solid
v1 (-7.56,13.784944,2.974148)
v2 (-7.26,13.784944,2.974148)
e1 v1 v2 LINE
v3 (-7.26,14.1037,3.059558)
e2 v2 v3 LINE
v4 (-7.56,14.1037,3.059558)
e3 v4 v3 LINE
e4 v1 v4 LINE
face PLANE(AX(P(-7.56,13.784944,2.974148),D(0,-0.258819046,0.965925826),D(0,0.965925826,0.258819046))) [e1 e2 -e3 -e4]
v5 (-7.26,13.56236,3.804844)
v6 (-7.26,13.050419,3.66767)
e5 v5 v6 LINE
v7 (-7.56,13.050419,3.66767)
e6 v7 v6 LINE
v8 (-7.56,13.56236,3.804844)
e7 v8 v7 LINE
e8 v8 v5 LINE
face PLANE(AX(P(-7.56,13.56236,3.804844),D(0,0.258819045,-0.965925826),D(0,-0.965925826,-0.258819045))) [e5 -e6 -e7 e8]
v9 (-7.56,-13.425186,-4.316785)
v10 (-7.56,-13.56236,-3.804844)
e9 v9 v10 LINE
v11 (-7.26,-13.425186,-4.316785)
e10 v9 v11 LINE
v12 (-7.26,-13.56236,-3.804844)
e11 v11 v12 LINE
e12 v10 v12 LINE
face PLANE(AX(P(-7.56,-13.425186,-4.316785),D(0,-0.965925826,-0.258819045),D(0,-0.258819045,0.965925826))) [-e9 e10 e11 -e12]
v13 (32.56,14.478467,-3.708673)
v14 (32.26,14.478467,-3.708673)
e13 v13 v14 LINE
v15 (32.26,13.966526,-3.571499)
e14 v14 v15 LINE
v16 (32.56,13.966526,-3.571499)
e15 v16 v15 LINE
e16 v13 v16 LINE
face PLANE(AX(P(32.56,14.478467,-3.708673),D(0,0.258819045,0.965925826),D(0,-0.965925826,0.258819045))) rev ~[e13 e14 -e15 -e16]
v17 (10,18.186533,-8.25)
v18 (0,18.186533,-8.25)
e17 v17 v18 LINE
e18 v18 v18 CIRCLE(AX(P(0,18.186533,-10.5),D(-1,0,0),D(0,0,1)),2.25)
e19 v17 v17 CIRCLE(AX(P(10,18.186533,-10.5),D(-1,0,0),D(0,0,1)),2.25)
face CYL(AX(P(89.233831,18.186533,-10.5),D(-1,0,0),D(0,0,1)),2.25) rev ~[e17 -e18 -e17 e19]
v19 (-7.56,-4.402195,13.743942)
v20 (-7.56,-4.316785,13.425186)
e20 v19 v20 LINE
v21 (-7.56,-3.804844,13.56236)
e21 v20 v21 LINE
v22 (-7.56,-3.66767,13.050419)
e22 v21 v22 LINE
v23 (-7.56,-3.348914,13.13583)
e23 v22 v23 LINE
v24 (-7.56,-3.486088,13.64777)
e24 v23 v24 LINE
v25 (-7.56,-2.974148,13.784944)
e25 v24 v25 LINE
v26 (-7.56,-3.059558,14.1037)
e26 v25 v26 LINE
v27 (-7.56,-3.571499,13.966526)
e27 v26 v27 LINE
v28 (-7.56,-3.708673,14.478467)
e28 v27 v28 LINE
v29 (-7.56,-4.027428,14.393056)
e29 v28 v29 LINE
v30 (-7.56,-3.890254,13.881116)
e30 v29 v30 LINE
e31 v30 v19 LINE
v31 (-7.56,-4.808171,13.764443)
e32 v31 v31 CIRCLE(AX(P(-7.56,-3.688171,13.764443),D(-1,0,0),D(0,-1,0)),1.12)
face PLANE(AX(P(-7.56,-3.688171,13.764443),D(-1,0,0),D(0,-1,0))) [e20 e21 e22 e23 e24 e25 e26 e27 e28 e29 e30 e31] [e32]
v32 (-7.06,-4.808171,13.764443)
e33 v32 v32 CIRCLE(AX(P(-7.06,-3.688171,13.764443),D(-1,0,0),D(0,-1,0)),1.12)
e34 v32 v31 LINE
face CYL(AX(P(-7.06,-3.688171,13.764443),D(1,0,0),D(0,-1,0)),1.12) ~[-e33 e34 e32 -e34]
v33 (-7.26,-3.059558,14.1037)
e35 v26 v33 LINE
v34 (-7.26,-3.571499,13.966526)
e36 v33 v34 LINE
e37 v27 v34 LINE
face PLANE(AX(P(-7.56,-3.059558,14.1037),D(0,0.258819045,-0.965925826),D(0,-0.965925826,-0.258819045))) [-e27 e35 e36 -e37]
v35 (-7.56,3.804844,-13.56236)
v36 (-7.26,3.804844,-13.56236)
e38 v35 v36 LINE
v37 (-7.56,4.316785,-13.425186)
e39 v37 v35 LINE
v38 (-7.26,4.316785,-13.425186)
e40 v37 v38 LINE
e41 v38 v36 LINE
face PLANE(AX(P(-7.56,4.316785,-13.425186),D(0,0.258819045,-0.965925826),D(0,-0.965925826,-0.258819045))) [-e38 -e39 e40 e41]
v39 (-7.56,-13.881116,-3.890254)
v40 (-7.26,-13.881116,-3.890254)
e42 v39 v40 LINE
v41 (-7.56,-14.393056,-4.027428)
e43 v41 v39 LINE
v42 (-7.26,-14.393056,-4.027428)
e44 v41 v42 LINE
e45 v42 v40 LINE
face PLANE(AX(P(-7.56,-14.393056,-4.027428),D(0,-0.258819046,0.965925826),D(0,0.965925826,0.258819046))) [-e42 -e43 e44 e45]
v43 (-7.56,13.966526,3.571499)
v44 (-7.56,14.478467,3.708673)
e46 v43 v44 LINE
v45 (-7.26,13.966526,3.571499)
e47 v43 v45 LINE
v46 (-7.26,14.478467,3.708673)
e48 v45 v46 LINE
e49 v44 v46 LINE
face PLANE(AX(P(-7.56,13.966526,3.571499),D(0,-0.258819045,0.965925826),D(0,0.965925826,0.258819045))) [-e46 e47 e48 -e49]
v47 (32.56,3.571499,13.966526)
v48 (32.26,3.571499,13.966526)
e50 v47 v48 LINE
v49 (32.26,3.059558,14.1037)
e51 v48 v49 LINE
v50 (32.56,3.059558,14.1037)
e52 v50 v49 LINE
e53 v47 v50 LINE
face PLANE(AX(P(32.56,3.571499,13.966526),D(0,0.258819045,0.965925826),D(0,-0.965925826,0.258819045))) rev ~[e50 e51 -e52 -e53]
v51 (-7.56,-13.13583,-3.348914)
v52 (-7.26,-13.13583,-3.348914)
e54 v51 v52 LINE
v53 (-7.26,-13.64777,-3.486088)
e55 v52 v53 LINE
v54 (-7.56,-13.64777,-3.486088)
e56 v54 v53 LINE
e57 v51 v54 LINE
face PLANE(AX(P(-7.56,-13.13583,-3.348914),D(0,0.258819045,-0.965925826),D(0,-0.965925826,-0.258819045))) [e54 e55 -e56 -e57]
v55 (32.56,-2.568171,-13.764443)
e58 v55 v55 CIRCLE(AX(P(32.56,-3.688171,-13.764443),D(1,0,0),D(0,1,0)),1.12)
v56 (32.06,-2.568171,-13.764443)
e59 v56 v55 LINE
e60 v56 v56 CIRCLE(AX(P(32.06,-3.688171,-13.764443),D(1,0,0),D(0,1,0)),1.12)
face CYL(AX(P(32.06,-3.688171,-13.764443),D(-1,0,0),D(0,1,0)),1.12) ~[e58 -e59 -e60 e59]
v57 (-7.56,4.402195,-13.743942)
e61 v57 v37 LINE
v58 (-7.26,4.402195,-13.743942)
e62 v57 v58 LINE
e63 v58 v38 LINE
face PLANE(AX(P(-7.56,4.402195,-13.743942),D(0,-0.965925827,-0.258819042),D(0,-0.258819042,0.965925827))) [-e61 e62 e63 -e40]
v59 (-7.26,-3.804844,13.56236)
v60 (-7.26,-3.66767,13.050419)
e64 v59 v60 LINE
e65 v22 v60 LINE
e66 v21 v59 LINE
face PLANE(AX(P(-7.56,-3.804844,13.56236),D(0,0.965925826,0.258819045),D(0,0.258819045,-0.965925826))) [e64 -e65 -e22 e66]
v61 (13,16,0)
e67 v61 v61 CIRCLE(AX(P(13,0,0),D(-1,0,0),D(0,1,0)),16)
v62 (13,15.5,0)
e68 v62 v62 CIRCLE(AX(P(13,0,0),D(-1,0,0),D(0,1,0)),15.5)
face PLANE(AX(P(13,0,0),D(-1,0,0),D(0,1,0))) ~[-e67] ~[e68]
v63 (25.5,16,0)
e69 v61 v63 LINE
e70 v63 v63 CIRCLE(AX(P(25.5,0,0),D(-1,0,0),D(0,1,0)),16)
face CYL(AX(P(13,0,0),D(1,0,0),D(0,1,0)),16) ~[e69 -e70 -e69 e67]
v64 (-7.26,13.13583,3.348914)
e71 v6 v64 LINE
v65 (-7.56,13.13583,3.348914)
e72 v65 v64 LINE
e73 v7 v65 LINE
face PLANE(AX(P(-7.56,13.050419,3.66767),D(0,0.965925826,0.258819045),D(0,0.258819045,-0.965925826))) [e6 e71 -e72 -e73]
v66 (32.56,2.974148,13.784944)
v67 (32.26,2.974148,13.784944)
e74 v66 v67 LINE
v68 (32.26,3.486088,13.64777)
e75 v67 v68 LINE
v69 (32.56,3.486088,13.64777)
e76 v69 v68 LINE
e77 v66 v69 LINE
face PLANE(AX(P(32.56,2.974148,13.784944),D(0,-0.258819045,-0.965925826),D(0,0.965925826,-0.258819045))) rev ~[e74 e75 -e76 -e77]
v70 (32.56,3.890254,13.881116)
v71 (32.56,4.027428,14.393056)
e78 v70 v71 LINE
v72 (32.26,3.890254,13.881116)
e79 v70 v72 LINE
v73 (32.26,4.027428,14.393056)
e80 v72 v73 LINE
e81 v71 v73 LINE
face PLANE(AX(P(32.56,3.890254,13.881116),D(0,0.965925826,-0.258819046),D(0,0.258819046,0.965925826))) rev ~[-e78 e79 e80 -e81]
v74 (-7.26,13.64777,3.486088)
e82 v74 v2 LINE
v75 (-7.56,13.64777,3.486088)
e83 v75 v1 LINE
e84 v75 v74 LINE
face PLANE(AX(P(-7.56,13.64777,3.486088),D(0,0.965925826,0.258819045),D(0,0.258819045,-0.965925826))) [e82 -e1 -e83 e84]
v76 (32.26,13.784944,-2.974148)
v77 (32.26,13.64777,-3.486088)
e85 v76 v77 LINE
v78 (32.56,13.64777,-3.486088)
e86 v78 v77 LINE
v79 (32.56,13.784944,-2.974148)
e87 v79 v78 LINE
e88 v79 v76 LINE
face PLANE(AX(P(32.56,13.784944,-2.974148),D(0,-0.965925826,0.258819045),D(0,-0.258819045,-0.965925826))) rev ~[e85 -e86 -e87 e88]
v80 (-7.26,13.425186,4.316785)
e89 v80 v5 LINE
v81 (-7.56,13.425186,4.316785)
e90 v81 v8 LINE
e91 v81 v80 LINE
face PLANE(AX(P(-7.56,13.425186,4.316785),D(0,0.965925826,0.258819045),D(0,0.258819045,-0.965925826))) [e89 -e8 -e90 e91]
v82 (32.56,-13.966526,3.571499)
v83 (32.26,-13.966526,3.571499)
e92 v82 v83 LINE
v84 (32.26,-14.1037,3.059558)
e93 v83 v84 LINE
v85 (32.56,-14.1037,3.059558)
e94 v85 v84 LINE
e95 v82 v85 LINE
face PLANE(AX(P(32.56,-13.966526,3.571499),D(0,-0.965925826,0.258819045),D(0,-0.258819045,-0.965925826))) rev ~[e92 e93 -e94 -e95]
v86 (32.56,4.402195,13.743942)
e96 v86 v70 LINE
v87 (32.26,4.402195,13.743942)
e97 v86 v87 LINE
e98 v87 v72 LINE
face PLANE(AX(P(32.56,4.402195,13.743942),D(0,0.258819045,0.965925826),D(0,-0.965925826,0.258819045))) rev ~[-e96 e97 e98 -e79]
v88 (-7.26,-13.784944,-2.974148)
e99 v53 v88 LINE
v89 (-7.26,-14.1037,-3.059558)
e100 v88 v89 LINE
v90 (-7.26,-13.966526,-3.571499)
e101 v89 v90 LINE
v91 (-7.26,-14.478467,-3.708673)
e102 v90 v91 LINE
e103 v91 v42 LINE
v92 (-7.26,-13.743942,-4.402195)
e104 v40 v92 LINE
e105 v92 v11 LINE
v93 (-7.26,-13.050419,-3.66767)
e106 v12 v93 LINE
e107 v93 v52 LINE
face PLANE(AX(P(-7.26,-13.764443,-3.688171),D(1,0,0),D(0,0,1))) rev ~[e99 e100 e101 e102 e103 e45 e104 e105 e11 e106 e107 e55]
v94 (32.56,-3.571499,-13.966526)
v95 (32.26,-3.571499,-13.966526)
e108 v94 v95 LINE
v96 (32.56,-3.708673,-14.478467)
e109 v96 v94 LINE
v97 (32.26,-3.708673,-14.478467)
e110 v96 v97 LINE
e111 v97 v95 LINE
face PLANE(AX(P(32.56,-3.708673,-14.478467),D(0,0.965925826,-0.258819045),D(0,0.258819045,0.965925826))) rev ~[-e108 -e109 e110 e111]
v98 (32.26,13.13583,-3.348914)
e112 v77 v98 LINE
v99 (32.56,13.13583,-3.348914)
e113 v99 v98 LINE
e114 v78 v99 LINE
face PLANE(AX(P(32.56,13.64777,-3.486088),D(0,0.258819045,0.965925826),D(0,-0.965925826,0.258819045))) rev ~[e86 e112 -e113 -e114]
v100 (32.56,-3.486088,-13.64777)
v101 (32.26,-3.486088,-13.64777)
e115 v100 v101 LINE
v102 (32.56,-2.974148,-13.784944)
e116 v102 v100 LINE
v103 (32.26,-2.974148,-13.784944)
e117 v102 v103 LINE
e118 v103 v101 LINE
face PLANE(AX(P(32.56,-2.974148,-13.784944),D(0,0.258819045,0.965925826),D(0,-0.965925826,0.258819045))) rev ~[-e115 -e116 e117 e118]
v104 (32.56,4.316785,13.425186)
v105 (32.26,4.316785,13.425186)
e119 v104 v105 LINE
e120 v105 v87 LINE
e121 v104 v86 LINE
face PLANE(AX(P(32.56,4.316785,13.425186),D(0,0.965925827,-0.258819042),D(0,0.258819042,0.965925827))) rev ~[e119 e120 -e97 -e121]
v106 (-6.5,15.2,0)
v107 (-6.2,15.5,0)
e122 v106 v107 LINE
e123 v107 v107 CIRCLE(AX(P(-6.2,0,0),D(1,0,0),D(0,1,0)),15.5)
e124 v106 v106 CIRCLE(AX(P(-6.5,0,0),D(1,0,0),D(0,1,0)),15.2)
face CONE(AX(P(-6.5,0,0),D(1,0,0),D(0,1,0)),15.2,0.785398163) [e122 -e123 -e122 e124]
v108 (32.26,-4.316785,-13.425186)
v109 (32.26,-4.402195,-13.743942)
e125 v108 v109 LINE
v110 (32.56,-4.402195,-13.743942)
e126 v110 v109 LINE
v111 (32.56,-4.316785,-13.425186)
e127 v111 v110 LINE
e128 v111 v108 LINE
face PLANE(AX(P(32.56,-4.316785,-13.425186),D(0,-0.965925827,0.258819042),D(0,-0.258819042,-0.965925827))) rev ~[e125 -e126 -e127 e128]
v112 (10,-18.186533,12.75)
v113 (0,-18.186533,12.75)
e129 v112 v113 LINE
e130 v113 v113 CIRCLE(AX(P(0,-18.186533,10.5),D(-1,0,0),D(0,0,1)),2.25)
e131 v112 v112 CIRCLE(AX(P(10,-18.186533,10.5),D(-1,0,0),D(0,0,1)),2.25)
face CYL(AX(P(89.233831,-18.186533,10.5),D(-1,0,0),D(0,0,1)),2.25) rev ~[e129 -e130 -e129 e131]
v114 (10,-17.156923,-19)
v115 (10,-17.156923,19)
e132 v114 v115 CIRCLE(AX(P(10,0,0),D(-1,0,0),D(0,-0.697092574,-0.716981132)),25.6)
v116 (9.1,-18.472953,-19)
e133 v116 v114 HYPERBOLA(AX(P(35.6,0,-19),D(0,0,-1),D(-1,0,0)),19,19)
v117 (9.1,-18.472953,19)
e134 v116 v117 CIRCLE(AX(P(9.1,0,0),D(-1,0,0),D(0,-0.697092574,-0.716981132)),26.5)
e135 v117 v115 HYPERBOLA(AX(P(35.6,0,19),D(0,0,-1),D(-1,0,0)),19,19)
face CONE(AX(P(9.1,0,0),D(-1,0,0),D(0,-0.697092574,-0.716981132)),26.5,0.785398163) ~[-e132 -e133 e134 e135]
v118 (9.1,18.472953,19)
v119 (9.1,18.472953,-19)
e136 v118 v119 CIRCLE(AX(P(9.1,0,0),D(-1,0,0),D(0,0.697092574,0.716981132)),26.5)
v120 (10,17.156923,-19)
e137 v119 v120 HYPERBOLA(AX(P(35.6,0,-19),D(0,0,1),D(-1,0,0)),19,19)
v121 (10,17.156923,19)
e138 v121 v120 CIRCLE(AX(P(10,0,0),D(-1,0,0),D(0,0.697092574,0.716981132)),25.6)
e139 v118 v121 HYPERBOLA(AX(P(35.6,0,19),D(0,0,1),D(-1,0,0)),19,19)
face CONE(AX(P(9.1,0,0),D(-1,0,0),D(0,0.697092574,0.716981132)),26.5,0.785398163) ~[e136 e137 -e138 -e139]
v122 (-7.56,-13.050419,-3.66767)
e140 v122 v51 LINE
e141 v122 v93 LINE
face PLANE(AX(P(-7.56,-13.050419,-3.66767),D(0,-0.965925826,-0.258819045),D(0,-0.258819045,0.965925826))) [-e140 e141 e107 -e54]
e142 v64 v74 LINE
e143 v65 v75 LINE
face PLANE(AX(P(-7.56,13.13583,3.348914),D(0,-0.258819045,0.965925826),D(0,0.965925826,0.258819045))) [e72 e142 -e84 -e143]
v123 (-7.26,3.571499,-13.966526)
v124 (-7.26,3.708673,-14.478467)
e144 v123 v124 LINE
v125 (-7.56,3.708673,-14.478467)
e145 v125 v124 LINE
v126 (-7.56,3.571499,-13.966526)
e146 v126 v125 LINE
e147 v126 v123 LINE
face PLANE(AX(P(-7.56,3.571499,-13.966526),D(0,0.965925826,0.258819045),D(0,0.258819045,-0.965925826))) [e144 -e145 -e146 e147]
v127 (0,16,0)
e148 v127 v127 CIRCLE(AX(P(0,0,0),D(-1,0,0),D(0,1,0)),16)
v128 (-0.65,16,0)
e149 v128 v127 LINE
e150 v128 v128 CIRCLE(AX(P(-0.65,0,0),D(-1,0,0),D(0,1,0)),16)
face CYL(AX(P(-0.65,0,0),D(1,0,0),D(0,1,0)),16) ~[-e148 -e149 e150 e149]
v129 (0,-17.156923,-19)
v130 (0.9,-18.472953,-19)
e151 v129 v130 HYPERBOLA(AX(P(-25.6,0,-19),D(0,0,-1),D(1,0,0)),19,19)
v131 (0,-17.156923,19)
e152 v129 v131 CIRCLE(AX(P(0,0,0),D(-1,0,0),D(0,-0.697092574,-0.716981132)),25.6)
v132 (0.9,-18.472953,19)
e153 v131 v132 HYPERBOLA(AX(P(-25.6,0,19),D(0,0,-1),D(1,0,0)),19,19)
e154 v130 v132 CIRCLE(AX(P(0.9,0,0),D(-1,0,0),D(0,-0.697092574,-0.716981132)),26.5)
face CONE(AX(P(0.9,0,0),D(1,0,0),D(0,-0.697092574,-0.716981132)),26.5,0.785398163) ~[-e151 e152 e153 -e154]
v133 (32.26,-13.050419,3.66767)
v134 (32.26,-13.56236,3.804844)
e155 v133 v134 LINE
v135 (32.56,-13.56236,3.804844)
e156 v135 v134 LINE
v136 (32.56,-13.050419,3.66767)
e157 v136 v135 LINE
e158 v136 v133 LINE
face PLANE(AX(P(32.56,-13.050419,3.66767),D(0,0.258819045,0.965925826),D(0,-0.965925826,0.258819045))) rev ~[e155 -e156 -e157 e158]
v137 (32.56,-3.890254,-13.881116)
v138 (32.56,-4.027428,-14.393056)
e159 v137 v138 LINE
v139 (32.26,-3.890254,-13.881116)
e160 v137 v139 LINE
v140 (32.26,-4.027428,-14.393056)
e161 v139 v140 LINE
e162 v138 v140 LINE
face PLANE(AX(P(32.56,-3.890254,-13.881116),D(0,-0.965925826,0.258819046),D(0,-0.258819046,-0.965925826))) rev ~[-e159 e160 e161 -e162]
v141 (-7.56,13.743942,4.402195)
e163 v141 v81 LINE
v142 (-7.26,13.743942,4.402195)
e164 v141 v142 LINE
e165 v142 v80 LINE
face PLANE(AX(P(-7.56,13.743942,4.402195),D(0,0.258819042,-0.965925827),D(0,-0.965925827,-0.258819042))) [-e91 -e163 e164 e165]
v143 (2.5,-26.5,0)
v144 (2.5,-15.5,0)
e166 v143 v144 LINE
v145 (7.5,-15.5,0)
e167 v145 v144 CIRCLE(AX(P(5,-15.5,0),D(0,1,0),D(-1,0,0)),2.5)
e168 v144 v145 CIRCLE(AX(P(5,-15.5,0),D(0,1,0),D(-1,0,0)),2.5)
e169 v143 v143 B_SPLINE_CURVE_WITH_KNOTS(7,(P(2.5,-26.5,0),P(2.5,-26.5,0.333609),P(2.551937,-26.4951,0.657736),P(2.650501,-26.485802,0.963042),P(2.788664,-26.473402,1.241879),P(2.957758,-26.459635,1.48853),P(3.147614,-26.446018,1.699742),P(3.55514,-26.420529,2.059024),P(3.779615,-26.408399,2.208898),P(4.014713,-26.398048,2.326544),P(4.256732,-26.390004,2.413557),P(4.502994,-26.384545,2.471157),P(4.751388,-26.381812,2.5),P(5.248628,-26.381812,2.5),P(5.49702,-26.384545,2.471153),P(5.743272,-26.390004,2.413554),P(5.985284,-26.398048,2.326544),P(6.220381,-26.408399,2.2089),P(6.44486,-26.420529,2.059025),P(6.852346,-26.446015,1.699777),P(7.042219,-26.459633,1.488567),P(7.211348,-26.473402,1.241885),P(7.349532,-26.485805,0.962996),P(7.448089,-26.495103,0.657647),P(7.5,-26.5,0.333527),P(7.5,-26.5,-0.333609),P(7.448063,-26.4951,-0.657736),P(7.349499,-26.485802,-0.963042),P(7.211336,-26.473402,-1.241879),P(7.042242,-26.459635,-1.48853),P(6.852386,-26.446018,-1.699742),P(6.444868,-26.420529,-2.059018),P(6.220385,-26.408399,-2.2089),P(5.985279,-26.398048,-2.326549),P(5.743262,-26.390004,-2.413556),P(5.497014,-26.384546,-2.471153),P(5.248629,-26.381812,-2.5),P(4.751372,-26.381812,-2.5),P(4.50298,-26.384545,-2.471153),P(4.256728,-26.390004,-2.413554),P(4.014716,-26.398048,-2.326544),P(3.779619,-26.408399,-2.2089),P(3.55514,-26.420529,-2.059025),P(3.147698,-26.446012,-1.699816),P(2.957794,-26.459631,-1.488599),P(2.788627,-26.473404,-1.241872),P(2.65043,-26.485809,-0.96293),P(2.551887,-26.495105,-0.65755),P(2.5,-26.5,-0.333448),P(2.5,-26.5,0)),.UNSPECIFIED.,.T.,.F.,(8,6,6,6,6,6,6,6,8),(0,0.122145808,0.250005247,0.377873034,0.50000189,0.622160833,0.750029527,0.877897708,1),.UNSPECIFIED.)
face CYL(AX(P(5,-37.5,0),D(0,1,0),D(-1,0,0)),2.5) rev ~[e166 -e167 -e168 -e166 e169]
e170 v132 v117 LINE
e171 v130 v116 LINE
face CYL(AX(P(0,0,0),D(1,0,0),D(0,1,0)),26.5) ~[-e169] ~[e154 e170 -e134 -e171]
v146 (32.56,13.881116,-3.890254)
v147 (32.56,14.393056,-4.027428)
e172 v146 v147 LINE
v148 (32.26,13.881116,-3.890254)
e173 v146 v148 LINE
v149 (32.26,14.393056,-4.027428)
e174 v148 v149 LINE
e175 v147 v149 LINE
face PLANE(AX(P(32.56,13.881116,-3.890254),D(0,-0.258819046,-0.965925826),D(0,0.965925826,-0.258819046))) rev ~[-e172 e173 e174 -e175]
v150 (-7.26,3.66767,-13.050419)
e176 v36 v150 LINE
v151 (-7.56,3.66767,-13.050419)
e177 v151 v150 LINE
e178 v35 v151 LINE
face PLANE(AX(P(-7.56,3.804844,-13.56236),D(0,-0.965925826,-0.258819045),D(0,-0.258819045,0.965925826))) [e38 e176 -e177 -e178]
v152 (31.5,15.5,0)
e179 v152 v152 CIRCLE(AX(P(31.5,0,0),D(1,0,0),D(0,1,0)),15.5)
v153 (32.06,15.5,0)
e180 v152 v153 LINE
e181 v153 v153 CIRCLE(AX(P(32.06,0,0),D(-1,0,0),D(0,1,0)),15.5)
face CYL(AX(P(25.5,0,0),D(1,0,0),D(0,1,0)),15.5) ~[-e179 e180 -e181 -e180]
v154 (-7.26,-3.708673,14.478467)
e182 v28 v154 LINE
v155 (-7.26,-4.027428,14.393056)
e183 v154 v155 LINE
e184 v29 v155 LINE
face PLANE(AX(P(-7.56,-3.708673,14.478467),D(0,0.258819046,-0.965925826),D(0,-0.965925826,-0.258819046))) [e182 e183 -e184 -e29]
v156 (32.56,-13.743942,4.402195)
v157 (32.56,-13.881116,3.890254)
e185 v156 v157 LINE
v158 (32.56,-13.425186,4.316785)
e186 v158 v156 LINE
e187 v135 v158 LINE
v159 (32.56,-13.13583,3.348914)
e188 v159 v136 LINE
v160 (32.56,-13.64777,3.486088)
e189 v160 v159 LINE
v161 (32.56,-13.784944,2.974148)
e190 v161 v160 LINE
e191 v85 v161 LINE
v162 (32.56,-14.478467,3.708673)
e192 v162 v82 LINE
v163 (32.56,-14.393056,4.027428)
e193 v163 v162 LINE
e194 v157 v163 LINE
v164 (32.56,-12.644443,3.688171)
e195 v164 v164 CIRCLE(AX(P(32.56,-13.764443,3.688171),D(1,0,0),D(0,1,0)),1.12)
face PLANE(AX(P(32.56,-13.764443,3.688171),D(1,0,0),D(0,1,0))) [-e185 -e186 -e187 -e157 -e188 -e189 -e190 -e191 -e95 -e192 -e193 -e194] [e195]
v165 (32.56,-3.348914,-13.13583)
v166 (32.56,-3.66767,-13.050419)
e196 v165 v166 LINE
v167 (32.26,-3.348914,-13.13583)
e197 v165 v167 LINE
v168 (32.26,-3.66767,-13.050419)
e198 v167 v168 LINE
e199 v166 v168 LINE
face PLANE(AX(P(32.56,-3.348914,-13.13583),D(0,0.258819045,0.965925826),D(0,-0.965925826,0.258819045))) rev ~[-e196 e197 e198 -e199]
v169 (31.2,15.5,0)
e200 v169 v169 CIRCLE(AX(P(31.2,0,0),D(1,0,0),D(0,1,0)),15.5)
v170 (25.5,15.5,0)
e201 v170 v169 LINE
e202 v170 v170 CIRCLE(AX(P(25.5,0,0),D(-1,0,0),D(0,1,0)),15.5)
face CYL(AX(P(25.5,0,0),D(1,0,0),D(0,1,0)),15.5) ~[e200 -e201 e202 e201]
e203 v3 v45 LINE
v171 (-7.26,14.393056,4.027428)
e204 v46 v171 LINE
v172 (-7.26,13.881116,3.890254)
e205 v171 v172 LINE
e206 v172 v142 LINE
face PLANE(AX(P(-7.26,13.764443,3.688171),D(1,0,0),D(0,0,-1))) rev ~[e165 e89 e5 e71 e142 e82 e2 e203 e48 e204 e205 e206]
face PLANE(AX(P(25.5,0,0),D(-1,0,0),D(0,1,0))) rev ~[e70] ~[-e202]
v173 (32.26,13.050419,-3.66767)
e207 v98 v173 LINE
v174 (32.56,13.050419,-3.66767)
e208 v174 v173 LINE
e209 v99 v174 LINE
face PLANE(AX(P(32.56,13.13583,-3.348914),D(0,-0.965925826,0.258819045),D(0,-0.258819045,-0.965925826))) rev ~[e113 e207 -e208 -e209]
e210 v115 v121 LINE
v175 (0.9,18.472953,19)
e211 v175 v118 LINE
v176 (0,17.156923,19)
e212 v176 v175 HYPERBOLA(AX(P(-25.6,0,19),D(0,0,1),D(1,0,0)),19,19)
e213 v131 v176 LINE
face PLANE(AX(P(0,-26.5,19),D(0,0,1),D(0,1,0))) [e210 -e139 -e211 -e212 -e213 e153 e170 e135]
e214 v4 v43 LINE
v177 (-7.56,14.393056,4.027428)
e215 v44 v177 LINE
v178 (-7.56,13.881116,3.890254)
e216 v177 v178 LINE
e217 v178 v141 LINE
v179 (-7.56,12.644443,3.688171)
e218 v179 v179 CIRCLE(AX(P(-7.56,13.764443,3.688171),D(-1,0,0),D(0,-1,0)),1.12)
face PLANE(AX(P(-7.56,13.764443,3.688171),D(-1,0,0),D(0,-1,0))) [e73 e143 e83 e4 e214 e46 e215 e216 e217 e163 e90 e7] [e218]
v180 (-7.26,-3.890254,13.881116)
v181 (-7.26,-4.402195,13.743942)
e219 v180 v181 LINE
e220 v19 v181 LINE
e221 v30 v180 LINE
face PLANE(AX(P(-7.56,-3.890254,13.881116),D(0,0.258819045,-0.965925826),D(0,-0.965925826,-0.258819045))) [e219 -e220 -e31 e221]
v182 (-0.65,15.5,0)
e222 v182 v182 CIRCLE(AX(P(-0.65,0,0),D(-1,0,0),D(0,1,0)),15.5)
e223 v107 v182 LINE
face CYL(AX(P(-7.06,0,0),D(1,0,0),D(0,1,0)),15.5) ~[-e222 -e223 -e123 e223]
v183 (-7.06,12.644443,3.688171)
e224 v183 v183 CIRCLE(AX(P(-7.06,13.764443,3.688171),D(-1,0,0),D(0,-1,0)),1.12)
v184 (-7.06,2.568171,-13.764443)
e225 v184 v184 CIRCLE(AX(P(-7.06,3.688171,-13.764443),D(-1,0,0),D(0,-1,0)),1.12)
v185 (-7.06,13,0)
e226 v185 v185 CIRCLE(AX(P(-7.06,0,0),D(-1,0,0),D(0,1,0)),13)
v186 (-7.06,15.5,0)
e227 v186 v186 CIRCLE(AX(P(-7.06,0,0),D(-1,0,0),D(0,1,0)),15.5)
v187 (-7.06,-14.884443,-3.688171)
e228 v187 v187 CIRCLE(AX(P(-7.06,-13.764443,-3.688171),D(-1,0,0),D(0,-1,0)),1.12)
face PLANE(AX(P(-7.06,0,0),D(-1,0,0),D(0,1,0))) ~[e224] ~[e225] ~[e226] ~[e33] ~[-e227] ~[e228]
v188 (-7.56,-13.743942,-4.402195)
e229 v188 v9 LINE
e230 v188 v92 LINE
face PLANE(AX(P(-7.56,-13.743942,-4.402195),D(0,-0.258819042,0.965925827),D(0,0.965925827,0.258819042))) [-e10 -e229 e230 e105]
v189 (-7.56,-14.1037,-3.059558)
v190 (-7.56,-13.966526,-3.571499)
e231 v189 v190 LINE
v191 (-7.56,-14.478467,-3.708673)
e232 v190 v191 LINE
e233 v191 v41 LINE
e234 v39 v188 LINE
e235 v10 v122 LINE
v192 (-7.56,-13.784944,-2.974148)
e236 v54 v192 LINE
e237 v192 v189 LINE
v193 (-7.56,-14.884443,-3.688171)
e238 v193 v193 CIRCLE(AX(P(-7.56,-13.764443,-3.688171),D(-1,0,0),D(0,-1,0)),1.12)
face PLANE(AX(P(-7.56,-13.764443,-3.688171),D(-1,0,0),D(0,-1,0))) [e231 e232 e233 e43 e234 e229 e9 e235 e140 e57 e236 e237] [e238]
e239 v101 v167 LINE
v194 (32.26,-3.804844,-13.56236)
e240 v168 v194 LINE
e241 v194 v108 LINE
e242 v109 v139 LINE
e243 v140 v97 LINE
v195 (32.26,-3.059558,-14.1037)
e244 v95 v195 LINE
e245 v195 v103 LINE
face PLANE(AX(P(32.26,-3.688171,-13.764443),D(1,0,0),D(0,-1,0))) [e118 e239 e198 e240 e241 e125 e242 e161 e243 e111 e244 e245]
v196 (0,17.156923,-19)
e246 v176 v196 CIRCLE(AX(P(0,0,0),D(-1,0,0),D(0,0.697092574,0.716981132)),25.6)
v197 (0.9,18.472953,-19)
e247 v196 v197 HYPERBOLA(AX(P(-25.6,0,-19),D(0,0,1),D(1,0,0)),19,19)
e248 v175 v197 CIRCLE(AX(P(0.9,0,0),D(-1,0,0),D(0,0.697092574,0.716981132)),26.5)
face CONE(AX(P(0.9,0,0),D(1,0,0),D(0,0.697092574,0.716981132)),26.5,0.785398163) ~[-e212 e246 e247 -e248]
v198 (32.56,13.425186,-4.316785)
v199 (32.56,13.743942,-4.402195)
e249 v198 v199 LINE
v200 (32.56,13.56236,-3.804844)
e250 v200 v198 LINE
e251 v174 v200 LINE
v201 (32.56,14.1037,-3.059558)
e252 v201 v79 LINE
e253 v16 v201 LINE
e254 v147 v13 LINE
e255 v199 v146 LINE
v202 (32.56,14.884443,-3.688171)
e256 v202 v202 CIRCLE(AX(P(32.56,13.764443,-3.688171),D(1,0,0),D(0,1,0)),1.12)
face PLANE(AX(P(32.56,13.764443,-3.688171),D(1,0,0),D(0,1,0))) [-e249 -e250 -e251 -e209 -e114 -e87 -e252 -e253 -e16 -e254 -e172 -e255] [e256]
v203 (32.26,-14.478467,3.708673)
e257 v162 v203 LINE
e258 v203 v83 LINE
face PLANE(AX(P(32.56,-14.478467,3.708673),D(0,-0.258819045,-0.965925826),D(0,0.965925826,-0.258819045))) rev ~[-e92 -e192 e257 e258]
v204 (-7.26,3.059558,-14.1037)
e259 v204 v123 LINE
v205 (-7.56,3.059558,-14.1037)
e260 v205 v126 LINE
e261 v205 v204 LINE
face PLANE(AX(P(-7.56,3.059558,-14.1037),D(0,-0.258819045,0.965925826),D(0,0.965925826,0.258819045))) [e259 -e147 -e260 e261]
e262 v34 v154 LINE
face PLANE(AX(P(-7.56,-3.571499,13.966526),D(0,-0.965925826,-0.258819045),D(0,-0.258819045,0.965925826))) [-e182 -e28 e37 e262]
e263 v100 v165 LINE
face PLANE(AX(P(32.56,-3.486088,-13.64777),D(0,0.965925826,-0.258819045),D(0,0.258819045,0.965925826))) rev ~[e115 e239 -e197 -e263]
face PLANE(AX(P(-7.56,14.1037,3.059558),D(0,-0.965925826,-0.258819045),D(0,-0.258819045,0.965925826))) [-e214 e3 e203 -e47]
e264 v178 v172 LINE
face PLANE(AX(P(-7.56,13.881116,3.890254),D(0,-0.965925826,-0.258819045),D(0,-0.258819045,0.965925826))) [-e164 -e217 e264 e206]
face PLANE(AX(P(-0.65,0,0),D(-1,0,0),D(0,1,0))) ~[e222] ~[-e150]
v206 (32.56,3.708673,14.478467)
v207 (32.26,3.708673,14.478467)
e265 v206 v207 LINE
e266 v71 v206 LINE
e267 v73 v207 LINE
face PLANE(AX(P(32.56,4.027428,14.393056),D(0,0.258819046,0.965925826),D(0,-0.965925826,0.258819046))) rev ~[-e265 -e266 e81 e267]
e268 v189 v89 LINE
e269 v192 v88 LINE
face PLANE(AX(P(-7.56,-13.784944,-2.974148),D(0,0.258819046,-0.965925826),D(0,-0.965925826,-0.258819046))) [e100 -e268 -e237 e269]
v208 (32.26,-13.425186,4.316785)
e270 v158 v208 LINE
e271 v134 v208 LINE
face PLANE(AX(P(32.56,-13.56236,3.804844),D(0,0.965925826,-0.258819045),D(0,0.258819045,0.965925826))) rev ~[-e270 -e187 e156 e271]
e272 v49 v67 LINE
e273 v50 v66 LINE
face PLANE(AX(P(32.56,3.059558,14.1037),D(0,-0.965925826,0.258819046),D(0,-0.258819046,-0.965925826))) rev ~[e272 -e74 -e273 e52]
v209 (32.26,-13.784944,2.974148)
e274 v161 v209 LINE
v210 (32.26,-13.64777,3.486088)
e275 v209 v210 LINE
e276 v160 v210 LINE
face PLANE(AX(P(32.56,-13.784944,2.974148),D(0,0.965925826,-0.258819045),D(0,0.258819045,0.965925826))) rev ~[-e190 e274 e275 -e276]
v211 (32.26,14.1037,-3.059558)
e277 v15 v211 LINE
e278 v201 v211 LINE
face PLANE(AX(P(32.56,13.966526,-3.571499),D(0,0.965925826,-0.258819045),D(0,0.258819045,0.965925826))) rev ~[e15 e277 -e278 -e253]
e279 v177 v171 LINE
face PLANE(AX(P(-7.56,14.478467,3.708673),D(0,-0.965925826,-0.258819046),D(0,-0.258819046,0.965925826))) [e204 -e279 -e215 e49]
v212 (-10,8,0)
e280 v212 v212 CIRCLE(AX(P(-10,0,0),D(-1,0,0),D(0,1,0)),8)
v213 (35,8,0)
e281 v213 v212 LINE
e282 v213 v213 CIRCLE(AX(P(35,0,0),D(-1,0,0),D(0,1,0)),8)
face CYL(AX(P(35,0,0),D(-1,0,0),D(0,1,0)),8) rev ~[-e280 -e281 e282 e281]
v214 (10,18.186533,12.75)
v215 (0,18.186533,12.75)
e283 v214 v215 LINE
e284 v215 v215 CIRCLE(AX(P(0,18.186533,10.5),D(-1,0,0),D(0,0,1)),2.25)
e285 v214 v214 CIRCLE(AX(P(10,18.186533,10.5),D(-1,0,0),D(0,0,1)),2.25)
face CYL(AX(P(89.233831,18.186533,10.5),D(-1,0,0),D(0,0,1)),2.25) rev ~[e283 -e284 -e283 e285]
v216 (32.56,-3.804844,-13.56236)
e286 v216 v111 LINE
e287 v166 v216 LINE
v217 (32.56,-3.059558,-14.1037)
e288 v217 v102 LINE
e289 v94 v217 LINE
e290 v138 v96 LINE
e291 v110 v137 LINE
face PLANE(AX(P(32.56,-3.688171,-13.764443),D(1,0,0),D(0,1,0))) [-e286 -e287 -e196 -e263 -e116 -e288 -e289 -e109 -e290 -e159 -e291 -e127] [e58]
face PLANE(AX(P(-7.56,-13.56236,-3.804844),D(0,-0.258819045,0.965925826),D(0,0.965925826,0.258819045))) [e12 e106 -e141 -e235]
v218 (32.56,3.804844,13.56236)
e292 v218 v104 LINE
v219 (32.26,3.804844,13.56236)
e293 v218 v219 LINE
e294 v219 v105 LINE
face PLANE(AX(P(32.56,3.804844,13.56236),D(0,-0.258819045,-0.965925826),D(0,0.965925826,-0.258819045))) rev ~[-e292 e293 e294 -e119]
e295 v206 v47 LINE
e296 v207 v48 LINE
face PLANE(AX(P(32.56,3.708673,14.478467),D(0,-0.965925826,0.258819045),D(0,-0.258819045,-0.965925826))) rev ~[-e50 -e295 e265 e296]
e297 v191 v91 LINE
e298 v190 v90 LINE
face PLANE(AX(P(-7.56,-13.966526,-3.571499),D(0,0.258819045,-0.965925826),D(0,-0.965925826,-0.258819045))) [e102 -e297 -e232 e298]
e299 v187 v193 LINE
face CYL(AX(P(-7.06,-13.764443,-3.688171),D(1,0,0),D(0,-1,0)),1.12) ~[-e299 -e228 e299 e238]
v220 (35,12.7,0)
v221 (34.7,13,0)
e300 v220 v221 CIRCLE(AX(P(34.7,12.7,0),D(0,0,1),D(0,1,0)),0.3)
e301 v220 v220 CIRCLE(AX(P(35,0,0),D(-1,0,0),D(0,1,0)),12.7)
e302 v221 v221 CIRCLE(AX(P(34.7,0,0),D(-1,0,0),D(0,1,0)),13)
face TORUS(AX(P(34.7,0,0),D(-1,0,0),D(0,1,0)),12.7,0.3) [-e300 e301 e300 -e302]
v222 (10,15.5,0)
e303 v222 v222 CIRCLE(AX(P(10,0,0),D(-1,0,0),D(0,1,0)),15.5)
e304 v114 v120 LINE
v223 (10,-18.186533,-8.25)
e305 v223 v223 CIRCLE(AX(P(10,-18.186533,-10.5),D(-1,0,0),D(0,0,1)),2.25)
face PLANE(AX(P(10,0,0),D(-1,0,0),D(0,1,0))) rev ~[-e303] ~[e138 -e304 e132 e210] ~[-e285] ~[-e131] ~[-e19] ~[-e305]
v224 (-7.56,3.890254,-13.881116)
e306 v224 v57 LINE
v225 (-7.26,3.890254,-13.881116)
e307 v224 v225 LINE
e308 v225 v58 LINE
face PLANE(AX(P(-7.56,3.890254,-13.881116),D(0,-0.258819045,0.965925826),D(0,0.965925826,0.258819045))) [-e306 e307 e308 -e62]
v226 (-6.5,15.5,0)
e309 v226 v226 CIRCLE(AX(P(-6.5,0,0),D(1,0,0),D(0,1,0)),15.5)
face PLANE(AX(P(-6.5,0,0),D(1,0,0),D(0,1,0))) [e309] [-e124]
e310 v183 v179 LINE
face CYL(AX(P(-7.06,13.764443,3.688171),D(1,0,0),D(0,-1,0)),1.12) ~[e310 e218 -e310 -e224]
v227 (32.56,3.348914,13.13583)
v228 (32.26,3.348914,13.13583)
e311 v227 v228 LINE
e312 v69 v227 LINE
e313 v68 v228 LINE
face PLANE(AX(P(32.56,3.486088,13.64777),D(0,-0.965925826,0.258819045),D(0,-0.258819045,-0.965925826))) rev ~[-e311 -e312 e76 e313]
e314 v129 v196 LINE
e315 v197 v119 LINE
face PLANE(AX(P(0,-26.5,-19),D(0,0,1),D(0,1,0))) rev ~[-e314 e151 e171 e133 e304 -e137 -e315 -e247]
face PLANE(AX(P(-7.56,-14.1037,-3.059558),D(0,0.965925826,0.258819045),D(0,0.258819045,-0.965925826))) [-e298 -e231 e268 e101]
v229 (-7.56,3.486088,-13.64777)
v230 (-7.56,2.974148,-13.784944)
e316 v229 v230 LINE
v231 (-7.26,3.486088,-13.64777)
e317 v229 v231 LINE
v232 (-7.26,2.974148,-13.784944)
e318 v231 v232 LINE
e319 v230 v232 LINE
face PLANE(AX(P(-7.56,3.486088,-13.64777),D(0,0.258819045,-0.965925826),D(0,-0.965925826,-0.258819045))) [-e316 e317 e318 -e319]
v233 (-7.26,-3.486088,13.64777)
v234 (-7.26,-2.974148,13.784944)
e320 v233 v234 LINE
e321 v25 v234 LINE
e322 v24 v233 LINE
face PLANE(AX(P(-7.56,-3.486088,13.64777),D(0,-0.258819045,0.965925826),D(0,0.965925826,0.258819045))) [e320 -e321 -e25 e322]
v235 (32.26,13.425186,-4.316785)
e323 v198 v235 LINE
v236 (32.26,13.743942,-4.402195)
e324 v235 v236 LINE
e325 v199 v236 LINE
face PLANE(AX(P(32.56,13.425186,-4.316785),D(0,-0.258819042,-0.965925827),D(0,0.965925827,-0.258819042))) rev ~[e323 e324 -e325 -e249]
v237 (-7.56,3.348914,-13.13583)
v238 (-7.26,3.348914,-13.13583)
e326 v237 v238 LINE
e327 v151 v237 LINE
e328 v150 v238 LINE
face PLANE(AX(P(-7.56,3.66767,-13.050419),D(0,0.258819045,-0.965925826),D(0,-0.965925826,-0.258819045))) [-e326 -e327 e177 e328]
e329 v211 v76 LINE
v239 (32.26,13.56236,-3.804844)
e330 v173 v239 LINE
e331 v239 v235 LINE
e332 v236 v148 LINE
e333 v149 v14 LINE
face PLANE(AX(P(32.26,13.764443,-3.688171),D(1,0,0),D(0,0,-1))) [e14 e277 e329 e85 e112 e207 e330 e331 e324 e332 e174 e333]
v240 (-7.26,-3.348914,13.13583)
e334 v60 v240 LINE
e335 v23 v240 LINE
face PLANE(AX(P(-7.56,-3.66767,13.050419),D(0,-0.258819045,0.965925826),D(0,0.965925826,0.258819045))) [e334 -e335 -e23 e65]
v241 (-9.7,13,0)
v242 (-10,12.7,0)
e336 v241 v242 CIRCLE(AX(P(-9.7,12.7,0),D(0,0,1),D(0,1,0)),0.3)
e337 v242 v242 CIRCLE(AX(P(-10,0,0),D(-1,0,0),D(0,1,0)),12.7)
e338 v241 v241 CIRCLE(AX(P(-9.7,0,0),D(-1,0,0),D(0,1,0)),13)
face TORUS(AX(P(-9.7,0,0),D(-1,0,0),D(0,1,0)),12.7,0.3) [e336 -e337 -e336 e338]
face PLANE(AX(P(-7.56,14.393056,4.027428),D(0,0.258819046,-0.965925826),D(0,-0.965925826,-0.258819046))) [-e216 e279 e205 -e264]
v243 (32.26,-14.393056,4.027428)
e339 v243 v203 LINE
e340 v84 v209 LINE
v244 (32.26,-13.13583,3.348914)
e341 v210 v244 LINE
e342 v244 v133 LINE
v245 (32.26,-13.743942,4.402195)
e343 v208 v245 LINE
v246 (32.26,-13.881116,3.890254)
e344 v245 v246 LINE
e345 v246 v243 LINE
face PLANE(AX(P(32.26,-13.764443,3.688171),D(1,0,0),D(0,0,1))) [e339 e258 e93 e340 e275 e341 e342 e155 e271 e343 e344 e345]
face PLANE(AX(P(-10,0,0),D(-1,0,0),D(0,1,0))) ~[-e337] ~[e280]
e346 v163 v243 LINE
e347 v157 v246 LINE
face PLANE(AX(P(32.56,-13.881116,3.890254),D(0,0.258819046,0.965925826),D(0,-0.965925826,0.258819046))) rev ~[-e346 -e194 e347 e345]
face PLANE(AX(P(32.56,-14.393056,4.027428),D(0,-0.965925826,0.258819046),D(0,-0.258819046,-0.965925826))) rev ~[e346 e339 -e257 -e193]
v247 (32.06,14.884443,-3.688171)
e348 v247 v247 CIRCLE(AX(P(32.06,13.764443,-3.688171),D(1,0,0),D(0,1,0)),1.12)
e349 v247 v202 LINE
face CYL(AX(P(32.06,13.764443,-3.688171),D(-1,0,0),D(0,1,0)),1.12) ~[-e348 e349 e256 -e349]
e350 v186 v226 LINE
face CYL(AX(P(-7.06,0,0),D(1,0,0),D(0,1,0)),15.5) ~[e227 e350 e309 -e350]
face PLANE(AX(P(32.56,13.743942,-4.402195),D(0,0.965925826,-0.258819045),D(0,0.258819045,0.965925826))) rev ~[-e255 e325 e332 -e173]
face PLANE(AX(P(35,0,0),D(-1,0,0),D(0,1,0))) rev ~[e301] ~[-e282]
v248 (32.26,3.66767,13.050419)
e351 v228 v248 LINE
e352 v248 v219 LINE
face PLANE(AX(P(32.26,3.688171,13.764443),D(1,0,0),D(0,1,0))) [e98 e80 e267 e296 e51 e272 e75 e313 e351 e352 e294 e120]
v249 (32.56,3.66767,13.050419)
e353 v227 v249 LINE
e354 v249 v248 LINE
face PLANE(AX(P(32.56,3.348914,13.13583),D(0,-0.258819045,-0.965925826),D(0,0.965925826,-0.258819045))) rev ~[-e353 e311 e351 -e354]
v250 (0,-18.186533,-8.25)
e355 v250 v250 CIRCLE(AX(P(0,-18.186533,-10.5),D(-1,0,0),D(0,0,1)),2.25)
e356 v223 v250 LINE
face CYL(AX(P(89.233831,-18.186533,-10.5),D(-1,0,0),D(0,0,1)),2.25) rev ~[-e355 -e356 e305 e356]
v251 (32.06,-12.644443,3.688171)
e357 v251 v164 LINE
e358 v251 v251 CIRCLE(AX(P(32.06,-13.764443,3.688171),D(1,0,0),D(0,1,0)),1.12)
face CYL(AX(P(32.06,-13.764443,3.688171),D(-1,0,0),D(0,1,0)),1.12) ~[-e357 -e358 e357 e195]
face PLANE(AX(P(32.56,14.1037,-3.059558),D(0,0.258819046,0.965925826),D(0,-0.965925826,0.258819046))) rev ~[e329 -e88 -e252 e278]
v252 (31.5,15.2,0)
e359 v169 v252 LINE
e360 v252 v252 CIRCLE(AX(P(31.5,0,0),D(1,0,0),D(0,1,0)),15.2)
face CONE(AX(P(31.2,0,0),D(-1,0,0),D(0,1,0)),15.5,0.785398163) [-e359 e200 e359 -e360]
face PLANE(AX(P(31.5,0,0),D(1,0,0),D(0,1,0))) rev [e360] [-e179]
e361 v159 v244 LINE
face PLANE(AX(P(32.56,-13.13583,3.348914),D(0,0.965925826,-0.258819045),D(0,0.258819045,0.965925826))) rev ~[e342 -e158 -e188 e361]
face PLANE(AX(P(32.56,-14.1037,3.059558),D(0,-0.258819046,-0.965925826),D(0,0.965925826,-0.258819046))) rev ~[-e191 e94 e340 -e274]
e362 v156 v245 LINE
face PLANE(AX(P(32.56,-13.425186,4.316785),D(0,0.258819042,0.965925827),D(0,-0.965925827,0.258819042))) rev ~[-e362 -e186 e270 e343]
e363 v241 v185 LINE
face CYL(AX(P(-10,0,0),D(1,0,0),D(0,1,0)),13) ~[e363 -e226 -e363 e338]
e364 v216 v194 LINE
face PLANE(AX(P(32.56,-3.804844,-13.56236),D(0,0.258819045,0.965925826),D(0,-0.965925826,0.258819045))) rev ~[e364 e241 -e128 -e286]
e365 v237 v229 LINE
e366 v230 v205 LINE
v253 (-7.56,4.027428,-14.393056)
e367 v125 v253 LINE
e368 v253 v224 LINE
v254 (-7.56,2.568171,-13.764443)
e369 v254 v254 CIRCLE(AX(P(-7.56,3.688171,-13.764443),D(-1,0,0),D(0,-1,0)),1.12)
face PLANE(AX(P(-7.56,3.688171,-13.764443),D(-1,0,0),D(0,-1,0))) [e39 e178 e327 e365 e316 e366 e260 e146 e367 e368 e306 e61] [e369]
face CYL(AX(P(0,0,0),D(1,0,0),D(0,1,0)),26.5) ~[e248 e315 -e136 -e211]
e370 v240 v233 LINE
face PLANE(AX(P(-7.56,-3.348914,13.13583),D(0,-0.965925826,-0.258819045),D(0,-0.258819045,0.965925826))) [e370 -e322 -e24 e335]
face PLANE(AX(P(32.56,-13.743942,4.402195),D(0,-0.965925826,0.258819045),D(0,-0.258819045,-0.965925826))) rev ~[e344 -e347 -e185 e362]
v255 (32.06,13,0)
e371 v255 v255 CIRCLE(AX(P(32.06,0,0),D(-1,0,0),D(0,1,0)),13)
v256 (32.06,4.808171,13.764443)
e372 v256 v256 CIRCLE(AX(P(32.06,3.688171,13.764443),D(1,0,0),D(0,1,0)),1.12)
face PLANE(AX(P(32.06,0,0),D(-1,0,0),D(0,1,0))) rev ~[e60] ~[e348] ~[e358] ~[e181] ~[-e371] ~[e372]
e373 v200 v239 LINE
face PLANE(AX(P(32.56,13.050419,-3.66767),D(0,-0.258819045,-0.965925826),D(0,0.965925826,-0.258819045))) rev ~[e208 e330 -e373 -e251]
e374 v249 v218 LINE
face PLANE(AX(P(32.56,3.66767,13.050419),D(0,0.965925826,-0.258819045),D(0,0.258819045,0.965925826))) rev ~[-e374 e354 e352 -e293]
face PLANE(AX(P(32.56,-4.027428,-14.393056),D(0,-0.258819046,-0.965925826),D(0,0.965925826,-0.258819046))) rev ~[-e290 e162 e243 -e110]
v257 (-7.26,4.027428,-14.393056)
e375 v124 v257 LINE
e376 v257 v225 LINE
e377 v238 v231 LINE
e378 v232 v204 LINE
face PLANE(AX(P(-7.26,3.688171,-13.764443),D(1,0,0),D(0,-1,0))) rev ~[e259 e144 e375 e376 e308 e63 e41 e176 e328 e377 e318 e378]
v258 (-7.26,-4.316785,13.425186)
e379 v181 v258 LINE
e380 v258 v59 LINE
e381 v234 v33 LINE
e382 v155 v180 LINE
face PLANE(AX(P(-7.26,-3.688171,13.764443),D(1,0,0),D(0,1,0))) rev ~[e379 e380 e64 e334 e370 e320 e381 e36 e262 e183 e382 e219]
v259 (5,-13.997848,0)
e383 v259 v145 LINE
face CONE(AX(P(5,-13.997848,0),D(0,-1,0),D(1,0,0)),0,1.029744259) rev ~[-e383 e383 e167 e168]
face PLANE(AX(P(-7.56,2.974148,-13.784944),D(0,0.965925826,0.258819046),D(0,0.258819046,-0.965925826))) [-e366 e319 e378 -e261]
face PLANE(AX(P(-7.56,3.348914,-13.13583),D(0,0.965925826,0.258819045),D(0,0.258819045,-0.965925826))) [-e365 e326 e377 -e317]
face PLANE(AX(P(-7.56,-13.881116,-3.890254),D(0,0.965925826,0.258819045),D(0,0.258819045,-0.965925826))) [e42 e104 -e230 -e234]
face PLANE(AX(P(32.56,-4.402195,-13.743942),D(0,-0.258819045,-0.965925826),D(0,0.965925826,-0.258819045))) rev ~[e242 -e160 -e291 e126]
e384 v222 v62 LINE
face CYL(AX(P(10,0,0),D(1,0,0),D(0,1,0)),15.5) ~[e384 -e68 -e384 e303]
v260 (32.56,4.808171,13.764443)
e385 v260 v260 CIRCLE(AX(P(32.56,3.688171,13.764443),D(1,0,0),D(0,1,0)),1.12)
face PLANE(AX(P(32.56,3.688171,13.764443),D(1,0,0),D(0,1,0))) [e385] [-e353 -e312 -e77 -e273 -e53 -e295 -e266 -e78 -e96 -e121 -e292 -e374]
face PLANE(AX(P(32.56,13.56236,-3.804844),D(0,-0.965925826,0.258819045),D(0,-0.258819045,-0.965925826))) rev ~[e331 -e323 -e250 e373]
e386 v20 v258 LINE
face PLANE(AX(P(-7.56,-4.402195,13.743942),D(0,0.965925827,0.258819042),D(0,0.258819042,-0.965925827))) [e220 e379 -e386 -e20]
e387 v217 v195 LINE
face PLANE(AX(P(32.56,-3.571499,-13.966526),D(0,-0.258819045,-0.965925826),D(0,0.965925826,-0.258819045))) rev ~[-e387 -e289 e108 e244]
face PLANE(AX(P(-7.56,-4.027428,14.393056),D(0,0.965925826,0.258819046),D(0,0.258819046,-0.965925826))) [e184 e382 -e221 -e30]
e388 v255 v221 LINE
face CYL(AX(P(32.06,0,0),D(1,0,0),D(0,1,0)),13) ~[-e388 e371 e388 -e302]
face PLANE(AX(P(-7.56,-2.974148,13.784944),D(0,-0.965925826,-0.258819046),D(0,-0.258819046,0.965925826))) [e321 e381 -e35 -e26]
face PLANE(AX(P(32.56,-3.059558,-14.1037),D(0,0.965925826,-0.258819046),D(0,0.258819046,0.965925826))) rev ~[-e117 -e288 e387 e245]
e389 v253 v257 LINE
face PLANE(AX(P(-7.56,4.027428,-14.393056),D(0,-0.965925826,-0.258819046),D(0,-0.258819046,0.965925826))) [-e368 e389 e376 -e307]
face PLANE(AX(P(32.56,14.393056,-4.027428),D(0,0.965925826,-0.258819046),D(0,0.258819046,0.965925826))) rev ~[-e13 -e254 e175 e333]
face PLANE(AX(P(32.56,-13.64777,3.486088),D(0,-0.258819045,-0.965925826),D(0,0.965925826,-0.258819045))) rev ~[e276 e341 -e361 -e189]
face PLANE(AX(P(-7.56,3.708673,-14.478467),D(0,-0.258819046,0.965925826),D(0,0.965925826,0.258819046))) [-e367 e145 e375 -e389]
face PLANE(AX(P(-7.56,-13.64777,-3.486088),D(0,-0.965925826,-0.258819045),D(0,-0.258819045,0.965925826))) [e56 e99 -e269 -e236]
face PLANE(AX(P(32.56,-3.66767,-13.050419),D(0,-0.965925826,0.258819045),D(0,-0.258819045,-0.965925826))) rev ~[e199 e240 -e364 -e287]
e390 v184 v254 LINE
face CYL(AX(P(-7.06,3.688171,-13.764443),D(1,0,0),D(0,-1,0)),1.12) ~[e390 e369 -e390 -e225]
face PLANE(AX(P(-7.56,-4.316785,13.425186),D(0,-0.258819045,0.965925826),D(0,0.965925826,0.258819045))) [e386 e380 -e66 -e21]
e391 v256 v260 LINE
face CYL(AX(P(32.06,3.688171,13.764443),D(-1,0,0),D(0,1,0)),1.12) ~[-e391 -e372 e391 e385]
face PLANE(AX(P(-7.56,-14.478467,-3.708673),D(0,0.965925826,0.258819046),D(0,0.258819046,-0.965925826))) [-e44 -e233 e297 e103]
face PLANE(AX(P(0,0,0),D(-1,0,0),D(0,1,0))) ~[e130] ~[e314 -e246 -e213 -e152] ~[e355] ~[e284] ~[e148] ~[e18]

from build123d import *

# Parameters (mm, degrees)
SKETCH2_OUTSIDE_W          = 72.484
SKETCH2_OUTSIDE_H          = 72.484
SKETCH2_OUTSIDE_W_2        = 38
SKETCH2_OUTSIDE_H_2        = 53
CUT_EXTRUDE1_DEPTH         = 52.278650528
F_4_5_4_5_DIAMETER_HOLE1_D = 4.5
SKETCH6_R                  = 1.12
BOSS_EXTRUDE1_DEPTH        = 0.5
CUT_EXTRUDE2_DEPTH         = 0.3
CIRPATTERN1_COUNT          = 4
SKETCH8_R                  = 1.12
BOSS_EXTRUDE2_DEPTH        = 0.5
CUT_EXTRUDE3_DEPTH         = 0.3
CIRPATTERN2_COUNT          = 4
M6_TAPPED_HOLE1_D          = 5
M6_TAPPED_HOLE1_DEPTH      = 11
M6_TAPPED_HOLE1_TIP        = 1.502151548
CHAMFER1_SIZE              = 0.9
FILLET1_R                  = 0.3


with BuildPart() as part:
    # Sketch1 → Revolve1 (revolve)
    with BuildSketch(Plane.XY):
        Polygon((35, 8), (-10, 8), (-10, 13), (-7.06, 13), (-7.06, 15.5), (-0.65, 15.5), (-0.65, 16), (0, 16), (0, 26.5), (10, 26.5), (10, 15.5), (13, 15.5), (13, 16), (25.5, 16), (25.5, 15.5), (32.06, 15.5), (32.06, 13), (35, 13), align=None)
    revolve(axis=Axis((35, 0, 0), (-1, 0, 0)))

    # Sketch2 outside → Cut-Extrude1 (cut, through all)
    with BuildSketch(Plane(origin=(0, 0, 0), x_dir=(0, 0, -1), z_dir=(1, 0, 0))):
        Rectangle(SKETCH2_OUTSIDE_W, SKETCH2_OUTSIDE_H)
        Rectangle(SKETCH2_OUTSIDE_W_2, SKETCH2_OUTSIDE_H_2, mode=Mode.SUBTRACT)
    extrude(amount=CUT_EXTRUDE1_DEPTH, mode=Mode.SUBTRACT)

    # Ø4.5 (4.5) Diameter Hole1 (through all)
    with Locations(Plane(origin=(10, 0, 0), x_dir=(0, 0, -1), z_dir=(1, 0, 0))):
        with Locations((-10.5, 18.186533479), (-10.5, -18.186533479), (10.5, 18.186533479), (10.5, -18.186533479)):
            Hole(F_4_5_4_5_DIAMETER_HOLE1_D / 2)

    # Sketch6 → Boss-Extrude1 (add)
    with BuildSketch(Plane(origin=(32.06, 0, 0), x_dir=(0, 0, -1), z_dir=(1, 0, 0))):
        with Locations(Location((3.688171393, 13.764443025, 0), (0, 0, 90))):
            Circle(SKETCH6_R)
        with Locations(Location((-13.764443025, 3.688171393, 0), (0, 0, 90))):
            Circle(SKETCH6_R)
        with Locations(Location((-3.688171393, -13.764443025, 0), (0, 0, 90))):
            Circle(SKETCH6_R)
        with Locations(Location((13.764443025, -3.688171393, 0), (0, 0, 90))):
            Circle(SKETCH6_R)
    extrude(amount=BOSS_EXTRUDE1_DEPTH)

    # Sketch7 → Cut-Extrude2 (cut)
    with BuildSketch(Plane(origin=(32.56, 0, 0), x_dir=(0, 0, -1), z_dir=(1, 0, 0))):
        Polygon((4.02742839, 14.393056331), (3.708672868, 14.478466616), (3.571498774, 13.966525928), (3.059558086, 14.103700022), (2.974147801, 13.7849445), (3.486088489, 13.647770406), (3.348914395, 13.135829718), (3.667669918, 13.050419433), (3.804844012, 13.562360121), (4.3167847, 13.425186027), (4.402194984, 13.74394155), (3.890254296, 13.881115644), align=None)
    cut_extrude2 = extrude(amount=-CUT_EXTRUDE2_DEPTH, mode=Mode.SUBTRACT)

    # CirPattern1: Cut-Extrude2 ×4 about axis
    cirpattern1_axis = Axis((0, 0, 0), (1, 0, 0))
    for i in range(1, CIRPATTERN1_COUNT):
        add(cut_extrude2.rotate(cirpattern1_axis, i * 360 / CIRPATTERN1_COUNT), mode=Mode.SUBTRACT)

    # Sketch8 → Boss-Extrude2 (add)
    with BuildSketch(Plane.ZY.offset(7.06)):
        with Locations(Location((3.688171393, 13.764443025, 0), (0, 0, 270))):
            Circle(SKETCH8_R)
        with Locations(Location((-13.764443025, 3.688171393, 0), (0, 0, 270))):
            Circle(SKETCH8_R)
        with Locations(Location((-3.688171393, -13.764443025, 0), (0, 0, 270))):
            Circle(SKETCH8_R)
        with Locations(Location((13.764443025, -3.688171393, 0), (0, 0, 270))):
            Circle(SKETCH8_R)
    extrude(amount=BOSS_EXTRUDE2_DEPTH)

    # Sketch9 → Cut-Extrude3 (cut)
    with BuildSketch(Plane.ZY.offset(7.56)):
        Polygon((3.571498774, 13.966525928), (3.708672868, 14.478466616), (4.02742839, 14.393056331), (3.890254296, 13.881115644), (4.402194984, 13.74394155), (4.3167847, 13.425186027), (3.804844012, 13.562360121), (3.667669918, 13.050419433), (3.348914395, 13.135829718), (3.486088489, 13.647770406), (2.974147801, 13.7849445), (3.059558086, 14.103700022), align=None)
    cut_extrude3 = extrude(amount=-CUT_EXTRUDE3_DEPTH, mode=Mode.SUBTRACT)

    # CirPattern2: Cut-Extrude3 ×4 about axis
    cirpattern2_axis = Axis((0, 0, 0), (1, 0, 0))
    for i in range(1, CIRPATTERN2_COUNT):
        add(cut_extrude3.rotate(cirpattern2_axis, i * 360 / CIRPATTERN2_COUNT), mode=Mode.SUBTRACT)

    # M6 Tapped Hole1
    with Locations(Plane.XZ.offset(26.5)):
        with Locations((5, 0)):
            Hole(M6_TAPPED_HOLE1_D / 2, depth=M6_TAPPED_HOLE1_DEPTH)
            with Locations((0, 0, -(M6_TAPPED_HOLE1_DEPTH + M6_TAPPED_HOLE1_TIP / 2))):  # 118° drill point
                Cone(0, M6_TAPPED_HOLE1_D / 2, M6_TAPPED_HOLE1_TIP, mode=Mode.SUBTRACT)

    # Sketch12 → Cut-Revolve1 (revolve, cut)
    with BuildSketch(Plane(origin=(0, 0, 0), x_dir=(1, 0, 0), z_dir=(0, 1, 0)), mode=Mode.PRIVATE) as cut_revolve1_sk:
        Polygon((31.2, -15.5), (31.5, -15.2), (31.5, -15.5), align=None)
        Polygon((-6.5, -15.5), (-6.5, -15.2), (-6.2, -15.5), align=None)
    revolve(cut_revolve1_sk.sketch.rotate(Axis((-12.404699919, 0, 0), (1, 0, 0)), 270), axis=Axis((-12.404699919, 0, 0), (1, 0, 0)), mode=Mode.SUBTRACT)

    # Chamfer1
    chamfer1_edges = [part.edges().sort_by_distance(p)[0] for p in [
        (10, 26.5, 0),
        (0, 26.5, 0),
        (10, -26.5, 0),
        (0, -26.5, 0),
    ]]
    chamfer(chamfer1_edges, length=CHAMFER1_SIZE)

    # Fillet1
    fillet1_edges = [part.edges().sort_by_distance(p)[0] for p in [
        (35, -13, 0),
        (-10, -13, 0),
    ]]
    fillet(fillet1_edges, radius=FILLET1_R)


solid = part.part
